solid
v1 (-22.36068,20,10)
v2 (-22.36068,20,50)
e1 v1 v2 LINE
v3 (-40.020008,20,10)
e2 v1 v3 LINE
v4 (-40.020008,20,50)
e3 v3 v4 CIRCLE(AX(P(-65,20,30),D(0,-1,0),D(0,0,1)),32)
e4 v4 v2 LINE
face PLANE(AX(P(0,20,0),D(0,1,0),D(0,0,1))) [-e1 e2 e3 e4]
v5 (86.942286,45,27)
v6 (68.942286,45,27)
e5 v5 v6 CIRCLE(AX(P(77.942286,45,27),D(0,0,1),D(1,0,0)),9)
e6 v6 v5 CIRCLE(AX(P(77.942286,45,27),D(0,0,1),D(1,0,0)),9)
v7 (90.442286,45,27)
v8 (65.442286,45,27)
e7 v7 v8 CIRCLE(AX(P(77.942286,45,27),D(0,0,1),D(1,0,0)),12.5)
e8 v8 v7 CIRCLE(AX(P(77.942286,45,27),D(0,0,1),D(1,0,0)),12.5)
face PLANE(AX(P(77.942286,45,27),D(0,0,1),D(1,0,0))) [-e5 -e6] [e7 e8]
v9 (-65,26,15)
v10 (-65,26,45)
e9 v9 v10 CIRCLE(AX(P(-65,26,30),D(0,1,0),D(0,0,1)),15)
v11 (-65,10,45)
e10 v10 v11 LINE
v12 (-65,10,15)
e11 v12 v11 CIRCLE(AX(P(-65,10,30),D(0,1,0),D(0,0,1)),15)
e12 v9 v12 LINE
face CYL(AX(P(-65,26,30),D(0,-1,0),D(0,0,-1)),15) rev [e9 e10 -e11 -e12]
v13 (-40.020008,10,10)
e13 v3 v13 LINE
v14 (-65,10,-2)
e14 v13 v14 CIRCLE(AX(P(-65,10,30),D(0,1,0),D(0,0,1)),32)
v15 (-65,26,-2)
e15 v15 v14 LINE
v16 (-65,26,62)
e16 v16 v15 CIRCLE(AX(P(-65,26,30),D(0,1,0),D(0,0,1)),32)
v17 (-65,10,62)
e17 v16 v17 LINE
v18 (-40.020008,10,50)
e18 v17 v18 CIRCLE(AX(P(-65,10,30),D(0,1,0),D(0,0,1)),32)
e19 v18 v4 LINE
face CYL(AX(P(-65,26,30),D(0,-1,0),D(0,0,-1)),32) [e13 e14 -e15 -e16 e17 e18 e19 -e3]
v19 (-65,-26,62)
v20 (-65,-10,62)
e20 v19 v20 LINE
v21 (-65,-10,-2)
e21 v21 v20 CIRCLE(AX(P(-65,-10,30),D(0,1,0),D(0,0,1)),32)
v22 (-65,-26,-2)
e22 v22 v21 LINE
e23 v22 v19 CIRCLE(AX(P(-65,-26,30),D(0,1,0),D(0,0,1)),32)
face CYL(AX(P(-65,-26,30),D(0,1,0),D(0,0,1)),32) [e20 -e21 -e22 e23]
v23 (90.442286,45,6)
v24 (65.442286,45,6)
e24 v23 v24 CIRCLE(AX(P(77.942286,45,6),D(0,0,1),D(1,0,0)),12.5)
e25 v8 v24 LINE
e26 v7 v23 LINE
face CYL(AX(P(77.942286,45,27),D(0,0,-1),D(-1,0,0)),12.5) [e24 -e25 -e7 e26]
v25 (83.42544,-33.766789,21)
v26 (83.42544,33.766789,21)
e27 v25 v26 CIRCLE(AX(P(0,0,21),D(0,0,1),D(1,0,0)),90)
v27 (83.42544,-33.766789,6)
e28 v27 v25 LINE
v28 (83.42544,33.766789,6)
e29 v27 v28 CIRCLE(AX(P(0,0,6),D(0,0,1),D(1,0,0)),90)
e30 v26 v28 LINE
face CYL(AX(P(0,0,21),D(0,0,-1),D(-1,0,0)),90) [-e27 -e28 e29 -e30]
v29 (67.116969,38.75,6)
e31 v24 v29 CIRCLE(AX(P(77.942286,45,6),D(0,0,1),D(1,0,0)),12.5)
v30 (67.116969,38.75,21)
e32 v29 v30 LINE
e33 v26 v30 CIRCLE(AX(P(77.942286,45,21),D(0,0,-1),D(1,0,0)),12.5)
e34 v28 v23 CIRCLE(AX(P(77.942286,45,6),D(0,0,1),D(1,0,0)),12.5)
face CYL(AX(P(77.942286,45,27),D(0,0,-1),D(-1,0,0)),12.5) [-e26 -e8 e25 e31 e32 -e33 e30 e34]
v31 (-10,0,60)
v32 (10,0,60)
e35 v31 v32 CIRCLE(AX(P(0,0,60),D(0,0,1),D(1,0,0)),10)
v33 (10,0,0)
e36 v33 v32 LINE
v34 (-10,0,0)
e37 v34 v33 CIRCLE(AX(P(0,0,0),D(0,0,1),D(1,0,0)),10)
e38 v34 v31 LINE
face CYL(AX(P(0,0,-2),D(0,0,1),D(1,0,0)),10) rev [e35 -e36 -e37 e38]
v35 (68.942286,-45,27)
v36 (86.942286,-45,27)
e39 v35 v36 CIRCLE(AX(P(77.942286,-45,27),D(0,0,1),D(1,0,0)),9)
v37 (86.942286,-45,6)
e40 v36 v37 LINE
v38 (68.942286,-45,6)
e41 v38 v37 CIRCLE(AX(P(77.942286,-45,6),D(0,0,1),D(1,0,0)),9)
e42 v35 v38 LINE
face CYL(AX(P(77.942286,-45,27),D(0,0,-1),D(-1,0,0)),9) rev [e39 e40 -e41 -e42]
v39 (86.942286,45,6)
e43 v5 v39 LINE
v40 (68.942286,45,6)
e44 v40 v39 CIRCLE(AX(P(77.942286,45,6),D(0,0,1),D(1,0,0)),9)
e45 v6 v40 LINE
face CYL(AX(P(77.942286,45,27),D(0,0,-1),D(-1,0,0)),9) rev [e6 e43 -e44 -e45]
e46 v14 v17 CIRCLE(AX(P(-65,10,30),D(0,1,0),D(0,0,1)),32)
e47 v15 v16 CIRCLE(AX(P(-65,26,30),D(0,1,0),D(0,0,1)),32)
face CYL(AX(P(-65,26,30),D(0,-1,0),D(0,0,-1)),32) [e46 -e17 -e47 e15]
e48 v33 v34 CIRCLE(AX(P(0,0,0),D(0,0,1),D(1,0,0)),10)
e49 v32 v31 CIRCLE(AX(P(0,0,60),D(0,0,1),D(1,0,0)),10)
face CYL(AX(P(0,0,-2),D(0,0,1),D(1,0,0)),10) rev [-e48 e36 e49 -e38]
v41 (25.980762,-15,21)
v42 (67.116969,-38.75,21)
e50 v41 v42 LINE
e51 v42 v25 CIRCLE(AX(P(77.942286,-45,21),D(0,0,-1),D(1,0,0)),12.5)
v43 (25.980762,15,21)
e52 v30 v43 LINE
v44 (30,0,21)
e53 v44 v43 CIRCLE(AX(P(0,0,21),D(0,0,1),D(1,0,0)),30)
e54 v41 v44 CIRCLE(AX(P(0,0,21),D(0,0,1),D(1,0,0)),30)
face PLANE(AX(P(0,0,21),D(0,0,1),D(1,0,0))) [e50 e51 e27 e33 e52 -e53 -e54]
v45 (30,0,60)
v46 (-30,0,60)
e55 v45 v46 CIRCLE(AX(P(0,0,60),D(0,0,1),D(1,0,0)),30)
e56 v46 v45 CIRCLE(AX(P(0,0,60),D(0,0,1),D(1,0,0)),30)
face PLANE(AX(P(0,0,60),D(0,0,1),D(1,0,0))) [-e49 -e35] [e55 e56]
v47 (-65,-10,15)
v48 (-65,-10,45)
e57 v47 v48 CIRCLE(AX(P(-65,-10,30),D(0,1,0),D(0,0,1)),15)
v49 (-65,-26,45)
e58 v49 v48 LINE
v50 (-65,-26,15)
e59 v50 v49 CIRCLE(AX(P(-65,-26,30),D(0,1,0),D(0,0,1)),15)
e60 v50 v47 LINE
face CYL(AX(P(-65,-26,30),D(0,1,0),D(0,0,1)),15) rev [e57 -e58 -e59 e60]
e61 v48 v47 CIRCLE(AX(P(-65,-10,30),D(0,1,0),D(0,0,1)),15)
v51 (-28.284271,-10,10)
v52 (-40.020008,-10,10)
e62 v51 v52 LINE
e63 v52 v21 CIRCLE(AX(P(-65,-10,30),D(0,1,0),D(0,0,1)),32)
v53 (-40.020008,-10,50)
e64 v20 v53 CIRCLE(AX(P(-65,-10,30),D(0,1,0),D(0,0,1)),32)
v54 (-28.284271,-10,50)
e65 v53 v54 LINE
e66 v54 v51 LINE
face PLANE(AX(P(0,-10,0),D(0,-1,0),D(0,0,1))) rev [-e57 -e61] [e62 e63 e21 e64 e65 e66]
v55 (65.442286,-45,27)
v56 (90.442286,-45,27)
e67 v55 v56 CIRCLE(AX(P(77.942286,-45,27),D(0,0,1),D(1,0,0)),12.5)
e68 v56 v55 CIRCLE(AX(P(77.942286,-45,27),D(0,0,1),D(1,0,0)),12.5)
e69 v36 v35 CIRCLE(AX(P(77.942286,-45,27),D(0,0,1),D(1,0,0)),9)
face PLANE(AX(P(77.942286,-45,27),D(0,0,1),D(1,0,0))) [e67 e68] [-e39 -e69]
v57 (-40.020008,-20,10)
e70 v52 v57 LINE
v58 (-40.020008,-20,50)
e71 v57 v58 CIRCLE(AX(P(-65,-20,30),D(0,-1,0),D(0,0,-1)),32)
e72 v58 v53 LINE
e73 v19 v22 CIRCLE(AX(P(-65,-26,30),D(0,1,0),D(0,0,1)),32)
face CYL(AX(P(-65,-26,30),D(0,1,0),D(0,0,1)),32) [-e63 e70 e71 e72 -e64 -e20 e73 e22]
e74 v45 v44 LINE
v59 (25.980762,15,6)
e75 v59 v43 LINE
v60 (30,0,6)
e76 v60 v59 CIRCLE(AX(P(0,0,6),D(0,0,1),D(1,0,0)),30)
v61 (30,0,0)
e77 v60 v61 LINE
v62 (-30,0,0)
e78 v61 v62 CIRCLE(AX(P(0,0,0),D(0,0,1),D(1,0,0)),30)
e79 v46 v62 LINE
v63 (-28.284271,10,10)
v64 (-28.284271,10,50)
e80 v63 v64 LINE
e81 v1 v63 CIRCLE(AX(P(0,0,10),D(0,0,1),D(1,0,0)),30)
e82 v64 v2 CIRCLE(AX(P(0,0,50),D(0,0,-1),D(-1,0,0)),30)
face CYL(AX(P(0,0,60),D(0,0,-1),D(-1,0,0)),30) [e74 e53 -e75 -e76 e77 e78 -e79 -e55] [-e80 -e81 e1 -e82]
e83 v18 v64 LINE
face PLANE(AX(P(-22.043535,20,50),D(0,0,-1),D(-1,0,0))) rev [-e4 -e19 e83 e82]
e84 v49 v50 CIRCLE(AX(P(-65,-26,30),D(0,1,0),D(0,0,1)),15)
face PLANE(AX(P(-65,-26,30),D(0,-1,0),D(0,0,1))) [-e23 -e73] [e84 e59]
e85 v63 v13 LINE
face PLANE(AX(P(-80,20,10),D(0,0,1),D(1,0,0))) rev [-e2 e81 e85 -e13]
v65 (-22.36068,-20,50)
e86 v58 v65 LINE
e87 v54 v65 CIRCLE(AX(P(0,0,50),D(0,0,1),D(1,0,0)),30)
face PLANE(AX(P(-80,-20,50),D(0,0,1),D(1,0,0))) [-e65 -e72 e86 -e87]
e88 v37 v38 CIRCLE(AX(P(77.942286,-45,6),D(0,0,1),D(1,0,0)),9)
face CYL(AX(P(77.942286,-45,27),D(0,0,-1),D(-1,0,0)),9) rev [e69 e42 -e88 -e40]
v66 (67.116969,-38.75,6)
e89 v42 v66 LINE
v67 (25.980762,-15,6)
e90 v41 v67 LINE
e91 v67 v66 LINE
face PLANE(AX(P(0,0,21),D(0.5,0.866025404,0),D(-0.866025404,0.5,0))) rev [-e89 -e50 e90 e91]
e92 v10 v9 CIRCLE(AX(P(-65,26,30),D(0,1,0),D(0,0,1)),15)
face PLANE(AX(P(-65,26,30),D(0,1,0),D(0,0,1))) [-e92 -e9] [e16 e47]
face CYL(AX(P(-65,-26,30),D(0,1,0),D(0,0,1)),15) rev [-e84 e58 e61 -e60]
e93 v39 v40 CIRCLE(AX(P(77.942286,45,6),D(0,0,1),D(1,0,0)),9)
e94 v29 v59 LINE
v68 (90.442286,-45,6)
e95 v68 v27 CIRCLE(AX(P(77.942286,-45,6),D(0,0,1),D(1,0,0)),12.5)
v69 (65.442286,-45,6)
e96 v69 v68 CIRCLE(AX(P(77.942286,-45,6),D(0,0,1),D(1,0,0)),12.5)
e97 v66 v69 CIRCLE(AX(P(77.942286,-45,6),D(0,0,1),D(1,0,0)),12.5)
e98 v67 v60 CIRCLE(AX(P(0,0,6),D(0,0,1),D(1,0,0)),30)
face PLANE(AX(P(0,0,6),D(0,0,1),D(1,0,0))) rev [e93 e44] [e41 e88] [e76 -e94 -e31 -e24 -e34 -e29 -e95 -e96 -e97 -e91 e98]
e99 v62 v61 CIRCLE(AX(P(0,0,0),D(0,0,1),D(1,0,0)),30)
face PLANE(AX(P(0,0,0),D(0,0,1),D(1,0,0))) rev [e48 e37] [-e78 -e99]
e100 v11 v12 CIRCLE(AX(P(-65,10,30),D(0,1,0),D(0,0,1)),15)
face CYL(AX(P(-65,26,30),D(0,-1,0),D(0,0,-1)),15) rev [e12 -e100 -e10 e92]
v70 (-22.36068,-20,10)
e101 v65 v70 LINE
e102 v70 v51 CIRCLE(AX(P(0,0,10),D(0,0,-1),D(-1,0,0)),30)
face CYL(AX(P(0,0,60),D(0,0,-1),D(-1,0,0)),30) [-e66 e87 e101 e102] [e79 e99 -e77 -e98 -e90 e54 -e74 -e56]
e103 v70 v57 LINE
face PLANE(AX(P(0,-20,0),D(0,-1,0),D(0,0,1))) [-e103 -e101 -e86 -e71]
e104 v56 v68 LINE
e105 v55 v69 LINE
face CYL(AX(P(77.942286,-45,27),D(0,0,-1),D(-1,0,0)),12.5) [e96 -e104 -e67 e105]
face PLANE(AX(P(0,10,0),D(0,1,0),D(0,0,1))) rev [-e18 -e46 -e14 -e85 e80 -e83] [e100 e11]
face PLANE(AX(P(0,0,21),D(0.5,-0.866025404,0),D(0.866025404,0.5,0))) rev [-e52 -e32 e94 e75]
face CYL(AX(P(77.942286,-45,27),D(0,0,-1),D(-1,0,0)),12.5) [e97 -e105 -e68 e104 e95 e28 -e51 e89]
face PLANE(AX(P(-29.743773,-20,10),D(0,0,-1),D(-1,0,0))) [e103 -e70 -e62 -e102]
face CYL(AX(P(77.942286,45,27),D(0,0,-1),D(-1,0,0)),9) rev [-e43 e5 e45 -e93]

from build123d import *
from build123d.topology import SkipClean

# Parameters (mm, degrees)
HUB_SKETCH_R               = 30
HUB_60_DEPTH               = 60
MOUNTING_ARM_DEPTH         = 15
UPPER_LUG_BOSS_SKETCH_R    = 12.5
UPPER_LUG_BOSS_SKETCH_R_2  = 9
UPPER_LUG_BOSS_25_DEPTH    = 21
UPPER_LUG_HOLE_DEPTH       = 113.138562317
CLEVIS_ARM_DEPTH           = 10
CLEVIS_EYE_BOSS_SKETCH_R   = 32
CLEVIS_EYE_BOSS_SKETCH_R_2 = 15
CLEVIS_EYE_BOSS_DEPTH      = 16
CLEVIS_EYE_HOLE_SKETCH_R   = 15
CLEVIS_EYE_HOLE_DEPTH      = 136.255314129
HUB_BORE_SKETCH_R          = 10
HUB_BORE_20_DEPTH          = 129.682749427
LOWER_LUG_BOSS_SKETCH_R    = 12.5
LOWER_LUG_BOSS_SKETCH_R_2  = 9
LOWER_LUG_BOSS_DEPTH       = 21
LOWER_LUG_HOLE_DEPTH       = 120.984373983


with BuildPart() as part:
    # Hub Sketch → Hub Ø60 (new body)
    with BuildSketch(Plane.XY):
        Circle(HUB_SKETCH_R)
    extrude(amount=HUB_60_DEPTH)

    # Mounting Arm Sketch → Mounting Arm (add)
    with BuildSketch(Plane.XY.offset(6)):
        with BuildLine():
            Line((0, 0), (77.942286341, 45))
            ThreePointArc((77.942286341, 45), (90, 0), (77.942286341, -45))
            Line((77.942286341, -45), (0, 0))
        make_face()
    extrude(amount=MOUNTING_ARM_DEPTH)

    # Upper Lug Boss Sketch → Upper Lug Boss Ø25 (add)
    with BuildSketch(Plane.XY.offset(6)):
        with Locations(Location((77.942286341, 45, 0), (0, 0, 210))):
            Circle(UPPER_LUG_BOSS_SKETCH_R)
        with Locations(Location((77.942286341, 45, 0), (0, 0, 210))):
            Circle(UPPER_LUG_BOSS_SKETCH_R_2, mode=Mode.SUBTRACT)
    extrude(amount=UPPER_LUG_BOSS_25_DEPTH)

    # Upper Lug Hole Sketch → Upper Lug Hole (cut, through all)
    with BuildSketch(Plane.XY.offset(27)):
        with BuildLine():
            Line((70.148057707, 40.5), (80.210020809, 46.309277106))
            Line((80.210020809, 46.309277106), (84.515342337, 38.852241476))
            ThreePointArc((84.515342337, 38.852241476), (76.916814405, 36.058612674), (70.148057707, 40.5))
        make_face()
    extrude(amount=-UPPER_LUG_HOLE_DEPTH, mode=Mode.SUBTRACT)

    # Clevis Arm Sketch → Clevis Arm (add)
    with BuildSketch(Plane(origin=(0, 10, 0), x_dir=(1, 0, 0), z_dir=(0, 1, 0))):
        Polygon((-29.743772899, -10), (-22.043534858, -10), (-22.043534858, -50), (-30, -50), (-80, -50), (-80, -40), (-65, -40), (-65, -20), (-80, -20), (-80, -10), align=None)
    clevis_arm = extrude(amount=CLEVIS_ARM_DEPTH)

    # Clevis Arm Mirror: Clevis Arm across plane
    add(clevis_arm.mirror(Plane.ZX))

    # Clevis Eye Boss Sketch → Clevis Eye Boss (add)
    with BuildSketch(Plane(origin=(0, 10, 0), x_dir=(1, 0, 0), z_dir=(0, 1, 0))):
        with Locations(Location((-65, -30, 0), (0, 0, 38.682187453))):
            Circle(CLEVIS_EYE_BOSS_SKETCH_R)
        with Locations(Location((-65, -30, 0), (0, 0, 138.189685104))):
            Circle(CLEVIS_EYE_BOSS_SKETCH_R_2, mode=Mode.SUBTRACT)
    clevis_eye_boss = extrude(amount=CLEVIS_EYE_BOSS_DEPTH)

    # Clevis Eye Boss Mirror: Clevis Eye Boss across plane
    add(clevis_eye_boss.mirror(Plane.ZX))

    # Clevis Eye Hole Sketch → Clevis Eye Hole (cut, through all)
    with SkipClean():  # the faces are left unmerged after this step: merging them gives an invalid solid
        with BuildSketch(Plane(origin=(0, 26, 0), x_dir=(1, 0, 0), z_dir=(0, 1, 0))):
            with Locations(Location((-65, -30, 0), (0, 0, 270))):
                Circle(CLEVIS_EYE_HOLE_SKETCH_R)
        extrude(amount=-CLEVIS_EYE_HOLE_DEPTH, mode=Mode.SUBTRACT)

    # Hub Bore Sketch → Hub Bore Ø20 (cut, through all)
    with SkipClean():  # the faces are left unmerged after this step: merging them gives an invalid solid
        with BuildSketch(Plane.XY.offset(60)):
            Circle(HUB_BORE_SKETCH_R)
        extrude(amount=-HUB_BORE_20_DEPTH, mode=Mode.SUBTRACT)

    # Lower Lug Boss Sketch → Lower Lug Boss (add)
    with SkipClean():  # the faces are left unmerged after this step: merging them gives an invalid solid
        with BuildSketch(Plane.XY.offset(6)):
            with Locations(Location((77.942286341, -45, 0), (0, 0, 150))):
                Circle(LOWER_LUG_BOSS_SKETCH_R)
            with Locations(Location((77.942286341, -45, 0), (0, 0, 150))):
                Circle(LOWER_LUG_BOSS_SKETCH_R_2, mode=Mode.SUBTRACT)
        extrude(amount=LOWER_LUG_BOSS_DEPTH)

    # Lower Lug Hole Sketch → Lower Lug Hole (cut, through all)
    with SkipClean():  # the faces are left unmerged after this step: merging them gives an invalid solid
        with BuildSketch(Plane.XY.offset(21)):
            with BuildLine():
                Line((77.942286341, -45), (70.148057707, -40.5))
                ThreePointArc((70.148057707, -40.5), (75.396242131, -36.367638858), (82.046946389, -36.990520249))
                ThreePointArc((82.046946389, -36.990520249), (80.094797514, -41.046600483), (77.942286341, -45))
            make_face()
        extrude(amount=-LOWER_LUG_HOLE_DEPTH, mode=Mode.SUBTRACT)


solid = part.part
